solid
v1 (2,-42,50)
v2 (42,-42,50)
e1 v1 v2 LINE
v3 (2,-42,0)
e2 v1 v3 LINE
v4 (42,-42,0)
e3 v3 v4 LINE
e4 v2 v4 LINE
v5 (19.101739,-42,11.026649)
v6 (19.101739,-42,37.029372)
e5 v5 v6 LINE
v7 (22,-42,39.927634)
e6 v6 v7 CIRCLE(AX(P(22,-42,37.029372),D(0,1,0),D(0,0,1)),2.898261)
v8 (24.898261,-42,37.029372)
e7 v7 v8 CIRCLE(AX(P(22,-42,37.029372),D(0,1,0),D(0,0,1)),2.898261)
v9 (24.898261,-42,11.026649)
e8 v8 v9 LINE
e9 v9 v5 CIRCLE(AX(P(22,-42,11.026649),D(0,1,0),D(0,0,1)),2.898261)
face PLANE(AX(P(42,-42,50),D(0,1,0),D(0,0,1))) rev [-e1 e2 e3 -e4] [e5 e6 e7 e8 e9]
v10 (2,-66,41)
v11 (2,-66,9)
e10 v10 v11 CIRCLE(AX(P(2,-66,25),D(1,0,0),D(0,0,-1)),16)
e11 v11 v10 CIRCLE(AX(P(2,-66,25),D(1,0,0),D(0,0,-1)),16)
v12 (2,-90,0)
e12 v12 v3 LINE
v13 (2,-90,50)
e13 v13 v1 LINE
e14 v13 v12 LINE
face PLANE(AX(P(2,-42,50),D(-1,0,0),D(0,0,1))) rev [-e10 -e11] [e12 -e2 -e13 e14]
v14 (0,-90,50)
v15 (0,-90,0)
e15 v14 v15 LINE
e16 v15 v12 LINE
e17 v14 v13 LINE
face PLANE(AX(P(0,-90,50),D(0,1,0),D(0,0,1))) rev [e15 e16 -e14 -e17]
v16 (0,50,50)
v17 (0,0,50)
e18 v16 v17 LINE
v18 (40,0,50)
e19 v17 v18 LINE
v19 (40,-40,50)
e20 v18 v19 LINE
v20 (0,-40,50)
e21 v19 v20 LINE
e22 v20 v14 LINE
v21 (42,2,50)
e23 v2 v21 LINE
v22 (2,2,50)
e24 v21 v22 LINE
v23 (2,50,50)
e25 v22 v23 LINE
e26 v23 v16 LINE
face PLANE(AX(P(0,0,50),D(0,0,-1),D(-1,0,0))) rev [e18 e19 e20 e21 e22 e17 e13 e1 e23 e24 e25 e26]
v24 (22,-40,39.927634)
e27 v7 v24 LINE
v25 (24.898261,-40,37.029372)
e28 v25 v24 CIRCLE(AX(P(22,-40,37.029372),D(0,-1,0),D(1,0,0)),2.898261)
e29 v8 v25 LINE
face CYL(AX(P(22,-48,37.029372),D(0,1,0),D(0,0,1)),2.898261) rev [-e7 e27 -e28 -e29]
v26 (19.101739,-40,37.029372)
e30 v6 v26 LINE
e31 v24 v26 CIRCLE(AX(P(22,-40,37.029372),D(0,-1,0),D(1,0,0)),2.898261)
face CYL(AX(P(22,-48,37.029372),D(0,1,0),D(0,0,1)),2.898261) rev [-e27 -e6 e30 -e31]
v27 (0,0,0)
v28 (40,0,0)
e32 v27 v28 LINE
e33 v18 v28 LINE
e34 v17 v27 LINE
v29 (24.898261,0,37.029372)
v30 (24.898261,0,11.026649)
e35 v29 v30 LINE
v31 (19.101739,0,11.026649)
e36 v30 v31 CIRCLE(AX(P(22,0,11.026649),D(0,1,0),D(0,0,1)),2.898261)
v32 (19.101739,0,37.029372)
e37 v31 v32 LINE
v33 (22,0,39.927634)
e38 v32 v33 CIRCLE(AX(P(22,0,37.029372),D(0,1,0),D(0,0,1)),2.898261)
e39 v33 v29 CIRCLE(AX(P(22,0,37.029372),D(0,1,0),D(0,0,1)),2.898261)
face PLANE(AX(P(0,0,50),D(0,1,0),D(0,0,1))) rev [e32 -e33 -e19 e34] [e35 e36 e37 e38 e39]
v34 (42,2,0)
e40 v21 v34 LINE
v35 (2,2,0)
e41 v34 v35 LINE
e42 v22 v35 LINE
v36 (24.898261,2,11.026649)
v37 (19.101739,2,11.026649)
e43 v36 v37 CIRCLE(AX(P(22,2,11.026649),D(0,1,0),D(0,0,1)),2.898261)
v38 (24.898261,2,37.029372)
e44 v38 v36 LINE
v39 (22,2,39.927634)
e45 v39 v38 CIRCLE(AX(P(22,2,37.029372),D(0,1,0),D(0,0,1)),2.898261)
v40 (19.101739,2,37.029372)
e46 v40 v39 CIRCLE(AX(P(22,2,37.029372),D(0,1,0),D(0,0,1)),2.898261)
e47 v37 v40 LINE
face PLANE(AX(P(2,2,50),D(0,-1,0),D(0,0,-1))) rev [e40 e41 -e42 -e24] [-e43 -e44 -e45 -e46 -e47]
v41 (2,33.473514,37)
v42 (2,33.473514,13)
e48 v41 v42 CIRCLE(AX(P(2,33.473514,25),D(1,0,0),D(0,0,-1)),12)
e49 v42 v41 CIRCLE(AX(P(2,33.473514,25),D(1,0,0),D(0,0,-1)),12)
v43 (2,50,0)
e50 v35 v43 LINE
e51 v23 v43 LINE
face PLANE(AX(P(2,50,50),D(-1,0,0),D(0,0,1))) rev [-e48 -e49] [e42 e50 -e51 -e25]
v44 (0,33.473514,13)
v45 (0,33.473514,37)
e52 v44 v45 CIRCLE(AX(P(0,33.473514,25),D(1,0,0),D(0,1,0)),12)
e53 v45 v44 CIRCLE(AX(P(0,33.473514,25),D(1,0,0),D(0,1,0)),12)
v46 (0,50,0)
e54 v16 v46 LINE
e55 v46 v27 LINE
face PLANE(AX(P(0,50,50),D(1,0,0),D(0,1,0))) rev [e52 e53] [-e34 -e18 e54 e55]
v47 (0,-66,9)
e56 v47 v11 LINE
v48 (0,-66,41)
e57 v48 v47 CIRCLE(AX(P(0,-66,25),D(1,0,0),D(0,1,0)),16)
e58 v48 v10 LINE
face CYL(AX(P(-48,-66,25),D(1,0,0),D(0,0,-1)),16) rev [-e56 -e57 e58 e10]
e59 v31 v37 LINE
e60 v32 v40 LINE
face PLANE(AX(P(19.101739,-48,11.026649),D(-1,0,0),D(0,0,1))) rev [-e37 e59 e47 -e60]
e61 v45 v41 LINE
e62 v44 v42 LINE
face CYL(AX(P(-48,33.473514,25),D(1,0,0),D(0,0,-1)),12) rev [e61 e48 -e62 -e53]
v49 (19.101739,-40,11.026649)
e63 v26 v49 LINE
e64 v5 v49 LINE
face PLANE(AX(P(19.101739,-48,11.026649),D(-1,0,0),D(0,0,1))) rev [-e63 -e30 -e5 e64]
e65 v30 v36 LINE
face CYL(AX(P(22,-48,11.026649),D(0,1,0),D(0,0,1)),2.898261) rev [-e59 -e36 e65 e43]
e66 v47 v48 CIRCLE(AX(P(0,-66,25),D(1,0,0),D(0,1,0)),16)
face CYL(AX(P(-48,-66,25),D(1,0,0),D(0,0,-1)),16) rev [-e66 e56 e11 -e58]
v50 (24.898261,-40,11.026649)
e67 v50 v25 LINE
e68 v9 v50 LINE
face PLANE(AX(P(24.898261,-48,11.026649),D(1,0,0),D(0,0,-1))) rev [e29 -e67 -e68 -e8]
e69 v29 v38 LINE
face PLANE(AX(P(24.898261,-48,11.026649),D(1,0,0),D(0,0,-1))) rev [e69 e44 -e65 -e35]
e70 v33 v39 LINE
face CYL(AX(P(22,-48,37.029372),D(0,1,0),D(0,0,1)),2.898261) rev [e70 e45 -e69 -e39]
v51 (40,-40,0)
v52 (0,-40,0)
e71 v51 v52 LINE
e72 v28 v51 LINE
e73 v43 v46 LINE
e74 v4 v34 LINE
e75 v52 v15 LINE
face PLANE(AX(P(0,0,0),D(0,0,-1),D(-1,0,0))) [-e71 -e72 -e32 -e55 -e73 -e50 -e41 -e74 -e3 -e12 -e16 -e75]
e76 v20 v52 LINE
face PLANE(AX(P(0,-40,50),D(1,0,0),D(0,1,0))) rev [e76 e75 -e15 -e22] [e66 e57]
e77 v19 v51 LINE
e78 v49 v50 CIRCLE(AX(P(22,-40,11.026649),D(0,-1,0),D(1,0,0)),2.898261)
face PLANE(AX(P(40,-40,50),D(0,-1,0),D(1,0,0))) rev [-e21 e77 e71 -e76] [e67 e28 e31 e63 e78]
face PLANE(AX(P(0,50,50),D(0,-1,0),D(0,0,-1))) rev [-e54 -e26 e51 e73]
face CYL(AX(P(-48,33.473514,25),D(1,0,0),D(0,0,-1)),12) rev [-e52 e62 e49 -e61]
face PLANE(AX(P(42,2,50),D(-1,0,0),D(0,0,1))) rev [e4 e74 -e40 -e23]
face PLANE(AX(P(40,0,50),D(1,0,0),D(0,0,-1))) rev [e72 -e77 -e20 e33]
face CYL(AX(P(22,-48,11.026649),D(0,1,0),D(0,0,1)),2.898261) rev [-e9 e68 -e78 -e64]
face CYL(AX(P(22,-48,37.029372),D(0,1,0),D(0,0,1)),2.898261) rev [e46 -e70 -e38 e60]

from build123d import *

# Parameters (mm, degrees)
BOSS_EXTRUDE1_DEPTH = 50
CUT_EXTRUDE1_DEPTH  = 50
SKETCH3_R           = 16
CUT_EXTRUDE2_DEPTH  = 50
SKETCH4_R           = 12
CUT_EXTRUDE3_DEPTH  = 50


with BuildPart() as part:
    # Sketch1 → Boss-Extrude1 (new body)
    with BuildSketch(Plane.XY):
        Polygon((0, 50), (0, 0), (40, 0), (40, -40), (0, -40), (0, -90), (2, -90), (2, -42), (42, -42), (42, 2), (2, 2), (2, 50), align=None)
    extrude(amount=BOSS_EXTRUDE1_DEPTH)

    # Sketch2 → Cut-Extrude1 (cut)
    with BuildSketch(Plane(origin=(0, 2, 0), x_dir=(1, 0, 0), z_dir=(0, 1, 0))):
        with BuildLine():
            Line((24.898261367, -11.026648657), (24.898261367, -37.029372299))
            ThreePointArc((24.898261367, -37.029372299), (22, -39.927633667), (19.101738633, -37.029372299))
            Line((19.101738633, -37.029372299), (19.101738633, -11.026648657))
            ThreePointArc((19.101738633, -11.026648657), (22, -8.12838729), (24.898261367, -11.026648657))
        make_face()
    extrude(amount=-CUT_EXTRUDE1_DEPTH, mode=Mode.SUBTRACT)

    # Sketch3 → Cut-Extrude2 (cut)
    with BuildSketch(Plane(origin=(2, 0, 0), x_dir=(0, 0, -1), z_dir=(1, 0, 0))):
        with Locations((-25, -66)):
            Circle(SKETCH3_R)
    extrude(amount=-CUT_EXTRUDE2_DEPTH, mode=Mode.SUBTRACT)

    # Sketch4 → Cut-Extrude3 (cut)
    with BuildSketch(Plane(origin=(2, 0, 0), x_dir=(0, 0, -1), z_dir=(1, 0, 0))):
        with Locations((-25, 33.473514378)):
            Circle(SKETCH4_R)
    extrude(amount=-CUT_EXTRUDE3_DEPTH, mode=Mode.SUBTRACT)


solid = part.part
